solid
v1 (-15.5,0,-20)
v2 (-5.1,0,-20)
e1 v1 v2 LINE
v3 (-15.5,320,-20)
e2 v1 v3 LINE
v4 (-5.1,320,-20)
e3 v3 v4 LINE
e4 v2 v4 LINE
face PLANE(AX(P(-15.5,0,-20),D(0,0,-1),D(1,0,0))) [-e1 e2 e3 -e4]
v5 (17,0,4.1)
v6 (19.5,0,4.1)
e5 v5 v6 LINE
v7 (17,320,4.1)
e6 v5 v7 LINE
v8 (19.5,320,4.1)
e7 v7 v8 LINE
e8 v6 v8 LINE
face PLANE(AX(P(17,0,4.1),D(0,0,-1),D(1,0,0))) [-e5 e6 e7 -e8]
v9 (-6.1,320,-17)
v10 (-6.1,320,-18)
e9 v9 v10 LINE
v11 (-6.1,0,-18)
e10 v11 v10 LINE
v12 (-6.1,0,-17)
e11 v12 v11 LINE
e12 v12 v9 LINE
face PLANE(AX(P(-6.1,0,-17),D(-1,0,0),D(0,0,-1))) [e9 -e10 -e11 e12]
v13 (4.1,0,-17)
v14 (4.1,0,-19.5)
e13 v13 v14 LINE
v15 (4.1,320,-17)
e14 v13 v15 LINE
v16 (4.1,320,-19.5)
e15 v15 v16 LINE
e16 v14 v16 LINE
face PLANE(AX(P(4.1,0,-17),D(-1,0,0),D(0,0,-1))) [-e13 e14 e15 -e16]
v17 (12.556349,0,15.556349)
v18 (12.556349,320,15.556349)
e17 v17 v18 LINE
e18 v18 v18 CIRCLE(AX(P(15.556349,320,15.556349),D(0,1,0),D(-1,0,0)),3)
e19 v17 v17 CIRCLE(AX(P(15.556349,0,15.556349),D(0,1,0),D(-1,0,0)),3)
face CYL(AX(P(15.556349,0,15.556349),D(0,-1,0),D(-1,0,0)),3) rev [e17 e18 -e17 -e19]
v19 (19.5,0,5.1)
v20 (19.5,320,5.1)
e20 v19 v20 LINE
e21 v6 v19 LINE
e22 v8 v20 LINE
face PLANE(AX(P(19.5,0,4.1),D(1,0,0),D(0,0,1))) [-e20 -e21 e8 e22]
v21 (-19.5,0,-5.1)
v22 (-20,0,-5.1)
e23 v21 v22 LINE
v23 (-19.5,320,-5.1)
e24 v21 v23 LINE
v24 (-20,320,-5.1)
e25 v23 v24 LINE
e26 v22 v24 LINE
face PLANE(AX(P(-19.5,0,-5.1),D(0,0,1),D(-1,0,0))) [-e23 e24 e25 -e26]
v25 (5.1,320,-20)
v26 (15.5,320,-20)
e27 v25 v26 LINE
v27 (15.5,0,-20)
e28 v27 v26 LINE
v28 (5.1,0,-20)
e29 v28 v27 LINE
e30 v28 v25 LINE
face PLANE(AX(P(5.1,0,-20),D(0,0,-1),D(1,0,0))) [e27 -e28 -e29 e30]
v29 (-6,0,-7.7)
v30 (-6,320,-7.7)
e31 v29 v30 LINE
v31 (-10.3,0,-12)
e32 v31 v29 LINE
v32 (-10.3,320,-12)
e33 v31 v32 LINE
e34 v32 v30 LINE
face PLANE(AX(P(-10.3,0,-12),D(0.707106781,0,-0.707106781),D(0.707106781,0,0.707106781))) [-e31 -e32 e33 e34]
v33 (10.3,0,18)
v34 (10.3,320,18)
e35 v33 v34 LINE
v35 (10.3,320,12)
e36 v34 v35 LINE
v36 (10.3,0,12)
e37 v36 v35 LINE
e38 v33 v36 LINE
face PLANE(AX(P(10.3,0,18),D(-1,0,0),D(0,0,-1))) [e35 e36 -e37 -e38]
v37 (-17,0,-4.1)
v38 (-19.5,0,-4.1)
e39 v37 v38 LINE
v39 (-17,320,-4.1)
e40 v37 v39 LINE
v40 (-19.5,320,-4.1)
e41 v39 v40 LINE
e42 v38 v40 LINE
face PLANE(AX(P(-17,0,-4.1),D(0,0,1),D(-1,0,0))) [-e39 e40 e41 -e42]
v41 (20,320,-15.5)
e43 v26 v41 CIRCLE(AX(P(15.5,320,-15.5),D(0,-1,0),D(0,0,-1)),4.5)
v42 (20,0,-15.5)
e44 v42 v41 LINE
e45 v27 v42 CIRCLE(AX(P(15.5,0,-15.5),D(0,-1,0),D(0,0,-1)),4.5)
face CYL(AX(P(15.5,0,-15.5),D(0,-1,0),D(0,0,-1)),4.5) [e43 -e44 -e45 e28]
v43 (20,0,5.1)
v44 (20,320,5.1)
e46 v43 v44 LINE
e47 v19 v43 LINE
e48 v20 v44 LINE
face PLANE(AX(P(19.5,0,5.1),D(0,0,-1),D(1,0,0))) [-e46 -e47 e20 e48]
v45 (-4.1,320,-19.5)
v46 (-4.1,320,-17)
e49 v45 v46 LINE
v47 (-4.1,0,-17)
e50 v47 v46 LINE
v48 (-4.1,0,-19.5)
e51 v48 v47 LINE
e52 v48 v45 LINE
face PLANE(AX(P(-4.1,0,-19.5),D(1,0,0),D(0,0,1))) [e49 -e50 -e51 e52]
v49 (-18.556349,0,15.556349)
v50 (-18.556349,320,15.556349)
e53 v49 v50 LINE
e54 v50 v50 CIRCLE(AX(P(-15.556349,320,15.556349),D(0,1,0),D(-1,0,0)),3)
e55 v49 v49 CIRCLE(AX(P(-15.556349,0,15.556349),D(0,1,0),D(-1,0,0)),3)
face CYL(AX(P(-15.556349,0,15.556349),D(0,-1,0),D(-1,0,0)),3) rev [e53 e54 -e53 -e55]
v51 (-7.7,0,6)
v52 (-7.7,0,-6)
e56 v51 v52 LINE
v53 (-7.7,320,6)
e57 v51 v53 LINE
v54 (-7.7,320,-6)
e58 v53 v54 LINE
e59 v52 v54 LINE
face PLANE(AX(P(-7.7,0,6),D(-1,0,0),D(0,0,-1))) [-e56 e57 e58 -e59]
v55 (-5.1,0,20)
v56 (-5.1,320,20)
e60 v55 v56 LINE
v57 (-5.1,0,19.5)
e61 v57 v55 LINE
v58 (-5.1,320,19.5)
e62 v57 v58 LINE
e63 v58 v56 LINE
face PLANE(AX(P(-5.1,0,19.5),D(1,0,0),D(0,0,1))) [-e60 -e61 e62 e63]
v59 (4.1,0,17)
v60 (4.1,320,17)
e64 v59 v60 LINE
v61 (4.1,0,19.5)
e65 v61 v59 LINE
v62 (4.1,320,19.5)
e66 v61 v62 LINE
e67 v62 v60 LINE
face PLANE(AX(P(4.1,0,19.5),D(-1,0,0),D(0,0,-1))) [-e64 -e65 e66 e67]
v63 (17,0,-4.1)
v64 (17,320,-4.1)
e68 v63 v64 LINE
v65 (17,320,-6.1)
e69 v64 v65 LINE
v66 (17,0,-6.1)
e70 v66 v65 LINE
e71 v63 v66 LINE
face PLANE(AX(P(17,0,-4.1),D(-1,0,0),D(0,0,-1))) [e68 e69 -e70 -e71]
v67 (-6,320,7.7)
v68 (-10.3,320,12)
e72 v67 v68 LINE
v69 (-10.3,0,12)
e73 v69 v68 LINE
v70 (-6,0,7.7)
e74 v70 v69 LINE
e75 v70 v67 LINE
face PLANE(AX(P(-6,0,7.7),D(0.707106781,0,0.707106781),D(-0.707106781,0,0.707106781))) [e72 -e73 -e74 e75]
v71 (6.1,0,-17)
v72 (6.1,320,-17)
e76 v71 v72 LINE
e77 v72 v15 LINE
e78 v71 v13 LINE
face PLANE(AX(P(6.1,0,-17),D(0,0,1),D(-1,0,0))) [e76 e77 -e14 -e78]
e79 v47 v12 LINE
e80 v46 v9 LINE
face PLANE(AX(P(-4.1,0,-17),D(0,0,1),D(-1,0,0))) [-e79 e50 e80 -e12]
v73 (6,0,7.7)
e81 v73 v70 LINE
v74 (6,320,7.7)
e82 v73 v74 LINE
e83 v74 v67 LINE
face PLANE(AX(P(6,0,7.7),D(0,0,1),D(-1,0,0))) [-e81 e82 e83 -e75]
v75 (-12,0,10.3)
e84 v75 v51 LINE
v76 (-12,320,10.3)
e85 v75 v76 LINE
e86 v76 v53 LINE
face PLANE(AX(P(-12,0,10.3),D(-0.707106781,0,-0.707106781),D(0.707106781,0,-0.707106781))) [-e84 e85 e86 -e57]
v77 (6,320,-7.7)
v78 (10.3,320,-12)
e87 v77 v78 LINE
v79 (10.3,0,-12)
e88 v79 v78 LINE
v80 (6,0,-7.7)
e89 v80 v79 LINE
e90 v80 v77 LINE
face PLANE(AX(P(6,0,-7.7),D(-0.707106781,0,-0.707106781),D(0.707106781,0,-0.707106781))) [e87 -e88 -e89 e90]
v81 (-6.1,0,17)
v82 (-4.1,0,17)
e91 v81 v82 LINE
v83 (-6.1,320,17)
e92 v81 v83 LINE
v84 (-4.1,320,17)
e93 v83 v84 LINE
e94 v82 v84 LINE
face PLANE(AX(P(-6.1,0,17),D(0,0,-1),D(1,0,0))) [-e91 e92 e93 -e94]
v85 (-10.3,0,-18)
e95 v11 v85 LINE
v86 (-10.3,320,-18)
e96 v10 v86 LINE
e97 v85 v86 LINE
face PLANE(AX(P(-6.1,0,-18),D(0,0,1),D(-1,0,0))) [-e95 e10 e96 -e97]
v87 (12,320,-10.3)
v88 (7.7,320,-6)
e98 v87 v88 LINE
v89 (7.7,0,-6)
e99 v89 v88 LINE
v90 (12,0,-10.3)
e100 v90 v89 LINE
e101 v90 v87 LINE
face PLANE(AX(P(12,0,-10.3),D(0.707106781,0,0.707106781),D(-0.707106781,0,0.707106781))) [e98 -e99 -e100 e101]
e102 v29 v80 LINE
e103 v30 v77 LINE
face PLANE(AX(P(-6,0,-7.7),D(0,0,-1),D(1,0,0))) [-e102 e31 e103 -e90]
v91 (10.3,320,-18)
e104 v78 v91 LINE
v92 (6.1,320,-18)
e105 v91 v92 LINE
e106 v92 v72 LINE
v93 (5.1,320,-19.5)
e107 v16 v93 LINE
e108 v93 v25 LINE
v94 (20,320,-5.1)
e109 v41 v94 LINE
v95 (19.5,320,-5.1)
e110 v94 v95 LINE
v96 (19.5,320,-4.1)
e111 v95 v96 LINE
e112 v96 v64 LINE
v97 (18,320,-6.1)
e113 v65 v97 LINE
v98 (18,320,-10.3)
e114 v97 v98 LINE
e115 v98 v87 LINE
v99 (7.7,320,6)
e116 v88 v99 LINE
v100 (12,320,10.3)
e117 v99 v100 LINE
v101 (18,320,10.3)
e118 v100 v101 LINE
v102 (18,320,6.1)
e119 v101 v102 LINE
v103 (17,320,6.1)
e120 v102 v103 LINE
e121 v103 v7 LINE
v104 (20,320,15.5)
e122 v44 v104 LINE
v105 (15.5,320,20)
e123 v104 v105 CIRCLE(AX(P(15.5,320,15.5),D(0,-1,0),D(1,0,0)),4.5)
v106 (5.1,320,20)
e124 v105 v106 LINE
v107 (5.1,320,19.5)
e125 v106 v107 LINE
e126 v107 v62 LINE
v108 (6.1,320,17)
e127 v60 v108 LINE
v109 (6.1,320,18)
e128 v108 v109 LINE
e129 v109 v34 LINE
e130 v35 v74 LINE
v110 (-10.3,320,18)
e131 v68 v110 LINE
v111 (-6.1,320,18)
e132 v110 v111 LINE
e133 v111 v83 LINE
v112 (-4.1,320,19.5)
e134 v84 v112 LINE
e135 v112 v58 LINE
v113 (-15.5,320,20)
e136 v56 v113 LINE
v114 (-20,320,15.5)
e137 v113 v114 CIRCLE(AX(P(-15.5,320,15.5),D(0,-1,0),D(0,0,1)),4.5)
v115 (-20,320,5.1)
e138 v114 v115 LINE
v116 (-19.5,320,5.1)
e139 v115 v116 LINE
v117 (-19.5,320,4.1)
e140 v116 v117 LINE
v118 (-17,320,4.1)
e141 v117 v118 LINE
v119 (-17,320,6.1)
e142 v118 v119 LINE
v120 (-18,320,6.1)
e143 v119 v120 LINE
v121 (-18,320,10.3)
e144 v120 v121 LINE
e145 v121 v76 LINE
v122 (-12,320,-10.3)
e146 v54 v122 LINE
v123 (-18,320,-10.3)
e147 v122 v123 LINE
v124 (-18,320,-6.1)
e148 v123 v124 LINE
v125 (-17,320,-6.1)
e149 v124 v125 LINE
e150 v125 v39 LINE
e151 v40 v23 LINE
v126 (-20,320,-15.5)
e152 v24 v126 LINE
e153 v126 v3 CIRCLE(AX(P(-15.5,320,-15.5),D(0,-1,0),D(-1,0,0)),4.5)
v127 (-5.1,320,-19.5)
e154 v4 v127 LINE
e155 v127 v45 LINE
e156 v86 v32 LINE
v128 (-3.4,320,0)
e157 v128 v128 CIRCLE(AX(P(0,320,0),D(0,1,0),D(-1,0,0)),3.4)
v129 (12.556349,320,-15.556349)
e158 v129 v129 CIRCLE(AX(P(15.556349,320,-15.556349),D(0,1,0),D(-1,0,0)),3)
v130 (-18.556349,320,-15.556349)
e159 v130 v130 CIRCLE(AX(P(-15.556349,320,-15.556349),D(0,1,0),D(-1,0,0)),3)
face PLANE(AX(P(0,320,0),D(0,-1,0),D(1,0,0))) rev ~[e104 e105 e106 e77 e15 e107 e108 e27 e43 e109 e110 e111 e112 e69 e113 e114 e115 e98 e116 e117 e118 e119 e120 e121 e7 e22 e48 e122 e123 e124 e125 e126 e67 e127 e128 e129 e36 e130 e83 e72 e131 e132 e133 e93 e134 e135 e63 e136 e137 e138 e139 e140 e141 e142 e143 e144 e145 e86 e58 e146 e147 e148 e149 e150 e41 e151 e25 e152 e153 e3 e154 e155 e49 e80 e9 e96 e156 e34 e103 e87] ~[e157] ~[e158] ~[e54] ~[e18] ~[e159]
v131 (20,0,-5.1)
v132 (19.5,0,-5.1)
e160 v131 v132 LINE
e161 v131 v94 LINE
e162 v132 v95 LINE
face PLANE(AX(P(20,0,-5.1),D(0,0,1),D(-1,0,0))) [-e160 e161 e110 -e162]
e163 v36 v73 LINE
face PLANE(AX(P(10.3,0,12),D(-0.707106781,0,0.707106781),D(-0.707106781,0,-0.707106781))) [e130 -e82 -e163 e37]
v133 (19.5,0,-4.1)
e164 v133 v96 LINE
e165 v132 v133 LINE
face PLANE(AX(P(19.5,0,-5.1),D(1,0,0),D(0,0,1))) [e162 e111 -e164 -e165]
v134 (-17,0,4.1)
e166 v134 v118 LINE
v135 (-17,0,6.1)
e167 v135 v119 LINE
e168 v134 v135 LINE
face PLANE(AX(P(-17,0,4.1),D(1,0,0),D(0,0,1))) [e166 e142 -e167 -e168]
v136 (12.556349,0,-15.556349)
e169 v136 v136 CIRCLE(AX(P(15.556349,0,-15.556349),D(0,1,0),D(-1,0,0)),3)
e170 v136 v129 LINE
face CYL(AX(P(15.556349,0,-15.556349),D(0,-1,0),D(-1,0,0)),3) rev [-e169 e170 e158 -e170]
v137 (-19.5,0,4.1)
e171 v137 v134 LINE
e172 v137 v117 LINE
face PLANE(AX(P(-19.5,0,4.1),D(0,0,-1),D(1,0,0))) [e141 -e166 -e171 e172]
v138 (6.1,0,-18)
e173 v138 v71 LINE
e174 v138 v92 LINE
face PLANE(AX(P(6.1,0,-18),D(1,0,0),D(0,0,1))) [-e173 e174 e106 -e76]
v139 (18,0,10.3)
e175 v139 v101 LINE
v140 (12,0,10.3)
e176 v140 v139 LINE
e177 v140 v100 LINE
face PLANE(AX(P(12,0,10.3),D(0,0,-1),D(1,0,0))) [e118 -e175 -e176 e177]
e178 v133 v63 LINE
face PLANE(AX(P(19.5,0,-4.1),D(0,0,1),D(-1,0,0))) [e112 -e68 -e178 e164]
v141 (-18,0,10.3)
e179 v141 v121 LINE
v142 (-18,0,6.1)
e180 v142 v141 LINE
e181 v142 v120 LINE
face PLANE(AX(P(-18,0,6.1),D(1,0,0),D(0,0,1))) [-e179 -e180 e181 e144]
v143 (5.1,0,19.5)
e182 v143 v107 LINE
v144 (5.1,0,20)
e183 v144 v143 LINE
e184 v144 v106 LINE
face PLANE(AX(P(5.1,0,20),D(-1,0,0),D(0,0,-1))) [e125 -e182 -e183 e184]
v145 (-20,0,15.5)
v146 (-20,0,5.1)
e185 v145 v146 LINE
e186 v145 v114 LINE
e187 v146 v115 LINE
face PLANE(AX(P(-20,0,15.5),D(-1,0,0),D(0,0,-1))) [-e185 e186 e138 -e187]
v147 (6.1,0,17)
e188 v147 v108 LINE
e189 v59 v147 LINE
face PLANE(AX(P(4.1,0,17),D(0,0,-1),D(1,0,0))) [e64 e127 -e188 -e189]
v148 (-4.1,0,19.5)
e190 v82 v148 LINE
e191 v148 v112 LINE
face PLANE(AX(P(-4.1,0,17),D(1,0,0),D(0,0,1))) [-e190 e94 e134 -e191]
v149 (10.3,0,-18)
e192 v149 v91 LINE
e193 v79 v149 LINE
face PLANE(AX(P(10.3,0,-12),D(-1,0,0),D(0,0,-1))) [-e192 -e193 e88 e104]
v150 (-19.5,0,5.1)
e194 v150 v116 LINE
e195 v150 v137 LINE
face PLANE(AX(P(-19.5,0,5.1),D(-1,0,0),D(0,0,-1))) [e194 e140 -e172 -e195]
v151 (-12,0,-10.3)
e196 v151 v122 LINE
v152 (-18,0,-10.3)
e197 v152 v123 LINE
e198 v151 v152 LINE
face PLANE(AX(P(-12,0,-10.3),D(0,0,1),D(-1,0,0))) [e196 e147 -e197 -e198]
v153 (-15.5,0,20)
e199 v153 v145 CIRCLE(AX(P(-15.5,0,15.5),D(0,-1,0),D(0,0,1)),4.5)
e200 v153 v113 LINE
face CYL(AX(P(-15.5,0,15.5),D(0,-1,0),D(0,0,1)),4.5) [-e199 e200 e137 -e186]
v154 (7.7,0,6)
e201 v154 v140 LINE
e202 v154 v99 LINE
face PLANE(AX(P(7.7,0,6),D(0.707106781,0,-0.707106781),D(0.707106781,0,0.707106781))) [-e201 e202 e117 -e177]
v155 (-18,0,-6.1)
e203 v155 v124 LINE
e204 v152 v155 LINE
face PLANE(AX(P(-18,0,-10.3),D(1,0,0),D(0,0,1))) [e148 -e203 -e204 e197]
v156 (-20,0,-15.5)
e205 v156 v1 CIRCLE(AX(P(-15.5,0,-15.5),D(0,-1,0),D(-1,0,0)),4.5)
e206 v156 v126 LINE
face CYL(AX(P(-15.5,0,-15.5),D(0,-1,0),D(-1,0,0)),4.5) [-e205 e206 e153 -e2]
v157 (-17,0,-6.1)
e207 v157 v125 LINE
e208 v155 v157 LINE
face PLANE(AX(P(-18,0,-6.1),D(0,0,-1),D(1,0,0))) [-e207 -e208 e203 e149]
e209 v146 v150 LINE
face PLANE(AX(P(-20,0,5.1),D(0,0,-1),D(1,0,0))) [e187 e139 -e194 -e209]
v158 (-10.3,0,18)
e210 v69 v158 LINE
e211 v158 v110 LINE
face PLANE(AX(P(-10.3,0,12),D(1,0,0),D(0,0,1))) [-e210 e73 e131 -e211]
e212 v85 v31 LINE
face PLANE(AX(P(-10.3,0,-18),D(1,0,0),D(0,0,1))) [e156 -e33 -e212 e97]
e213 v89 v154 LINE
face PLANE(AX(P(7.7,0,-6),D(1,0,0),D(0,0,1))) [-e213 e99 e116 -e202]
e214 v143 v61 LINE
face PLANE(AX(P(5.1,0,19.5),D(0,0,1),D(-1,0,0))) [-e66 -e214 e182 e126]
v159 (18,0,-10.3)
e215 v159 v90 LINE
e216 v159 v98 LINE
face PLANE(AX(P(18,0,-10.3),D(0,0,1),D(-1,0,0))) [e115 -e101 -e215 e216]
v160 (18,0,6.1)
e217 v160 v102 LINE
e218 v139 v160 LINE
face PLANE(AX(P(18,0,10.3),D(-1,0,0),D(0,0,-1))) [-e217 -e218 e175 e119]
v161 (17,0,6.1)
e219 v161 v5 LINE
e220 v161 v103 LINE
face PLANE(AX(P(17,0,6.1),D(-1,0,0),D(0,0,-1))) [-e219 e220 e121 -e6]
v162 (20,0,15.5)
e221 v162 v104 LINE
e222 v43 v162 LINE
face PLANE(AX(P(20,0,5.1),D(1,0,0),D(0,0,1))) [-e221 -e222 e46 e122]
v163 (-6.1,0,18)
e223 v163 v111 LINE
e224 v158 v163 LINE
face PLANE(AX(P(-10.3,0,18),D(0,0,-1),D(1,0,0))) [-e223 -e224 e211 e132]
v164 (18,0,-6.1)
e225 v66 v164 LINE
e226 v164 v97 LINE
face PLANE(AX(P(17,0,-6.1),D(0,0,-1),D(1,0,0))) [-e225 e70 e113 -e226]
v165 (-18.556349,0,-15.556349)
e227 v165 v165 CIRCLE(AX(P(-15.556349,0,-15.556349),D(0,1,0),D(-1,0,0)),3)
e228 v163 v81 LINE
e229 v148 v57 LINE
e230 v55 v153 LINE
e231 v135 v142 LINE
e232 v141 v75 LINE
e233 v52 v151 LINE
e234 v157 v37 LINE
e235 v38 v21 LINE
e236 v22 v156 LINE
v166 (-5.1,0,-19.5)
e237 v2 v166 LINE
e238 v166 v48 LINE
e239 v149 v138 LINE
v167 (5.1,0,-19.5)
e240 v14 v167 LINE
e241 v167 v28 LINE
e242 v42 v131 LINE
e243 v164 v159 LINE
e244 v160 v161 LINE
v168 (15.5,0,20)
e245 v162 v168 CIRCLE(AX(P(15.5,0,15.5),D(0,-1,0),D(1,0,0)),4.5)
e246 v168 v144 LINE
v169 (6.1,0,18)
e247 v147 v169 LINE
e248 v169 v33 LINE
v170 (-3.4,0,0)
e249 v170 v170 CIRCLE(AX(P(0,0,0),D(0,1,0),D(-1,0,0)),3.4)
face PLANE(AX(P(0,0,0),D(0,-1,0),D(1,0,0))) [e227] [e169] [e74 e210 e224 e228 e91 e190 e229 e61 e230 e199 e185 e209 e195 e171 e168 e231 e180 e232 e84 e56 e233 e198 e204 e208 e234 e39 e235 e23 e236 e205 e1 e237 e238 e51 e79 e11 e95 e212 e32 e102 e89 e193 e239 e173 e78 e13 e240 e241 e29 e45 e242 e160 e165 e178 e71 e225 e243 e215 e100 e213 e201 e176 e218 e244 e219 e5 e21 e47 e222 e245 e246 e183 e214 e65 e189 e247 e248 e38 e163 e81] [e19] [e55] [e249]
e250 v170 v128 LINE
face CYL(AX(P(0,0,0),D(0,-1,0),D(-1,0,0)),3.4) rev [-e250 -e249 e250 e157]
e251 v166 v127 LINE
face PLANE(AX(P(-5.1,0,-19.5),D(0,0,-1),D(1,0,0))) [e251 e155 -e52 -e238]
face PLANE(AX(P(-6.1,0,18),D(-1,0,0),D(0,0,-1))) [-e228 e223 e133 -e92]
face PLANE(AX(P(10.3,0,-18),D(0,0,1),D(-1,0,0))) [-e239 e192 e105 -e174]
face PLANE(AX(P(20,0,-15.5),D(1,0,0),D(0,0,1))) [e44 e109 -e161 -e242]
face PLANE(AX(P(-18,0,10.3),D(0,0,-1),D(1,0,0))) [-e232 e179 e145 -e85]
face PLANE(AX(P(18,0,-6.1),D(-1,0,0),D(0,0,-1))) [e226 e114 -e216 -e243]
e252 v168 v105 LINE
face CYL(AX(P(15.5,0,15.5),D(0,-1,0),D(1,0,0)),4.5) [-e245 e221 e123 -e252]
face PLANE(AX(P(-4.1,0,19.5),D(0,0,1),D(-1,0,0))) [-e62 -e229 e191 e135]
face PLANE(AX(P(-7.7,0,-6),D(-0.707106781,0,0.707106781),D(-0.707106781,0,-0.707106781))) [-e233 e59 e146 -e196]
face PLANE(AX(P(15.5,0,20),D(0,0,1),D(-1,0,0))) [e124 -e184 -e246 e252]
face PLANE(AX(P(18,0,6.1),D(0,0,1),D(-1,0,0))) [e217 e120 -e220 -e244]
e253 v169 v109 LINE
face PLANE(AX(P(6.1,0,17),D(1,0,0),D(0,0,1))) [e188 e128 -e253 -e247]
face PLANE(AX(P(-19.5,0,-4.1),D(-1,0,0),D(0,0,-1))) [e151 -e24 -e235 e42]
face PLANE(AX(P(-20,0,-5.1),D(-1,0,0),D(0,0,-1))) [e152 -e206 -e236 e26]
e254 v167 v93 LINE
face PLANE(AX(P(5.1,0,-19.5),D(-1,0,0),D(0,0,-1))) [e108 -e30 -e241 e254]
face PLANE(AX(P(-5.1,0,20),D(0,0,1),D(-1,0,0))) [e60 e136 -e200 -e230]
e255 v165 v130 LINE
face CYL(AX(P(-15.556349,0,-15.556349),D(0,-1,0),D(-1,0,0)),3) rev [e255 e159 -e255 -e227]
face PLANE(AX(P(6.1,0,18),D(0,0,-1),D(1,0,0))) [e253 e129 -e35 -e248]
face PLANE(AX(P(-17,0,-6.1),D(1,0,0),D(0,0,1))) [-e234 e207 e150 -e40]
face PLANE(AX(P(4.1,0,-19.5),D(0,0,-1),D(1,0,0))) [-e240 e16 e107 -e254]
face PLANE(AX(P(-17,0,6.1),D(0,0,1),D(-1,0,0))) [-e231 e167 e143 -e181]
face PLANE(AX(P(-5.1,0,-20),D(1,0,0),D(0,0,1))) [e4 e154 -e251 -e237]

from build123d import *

# Parameters (mm, degrees)
SKETCH16_R     = 3.4
SKETCH16_R_2   = 3
MEMBER_1_DEPTH = 320


with BuildPart() as part:
    # Sketch16 → Member 1 (new body)
    with BuildSketch(Plane(origin=(0, 0, 0), x_dir=(-1, 0, 0), z_dir=(0, 1, 0))):
        with BuildLine():
            Line((-5.1, 20), (-5.1, 19.5))
            Line((-5.1, 19.5), (-4.1, 19.5))
            Line((-4.1, 19.5), (-4.1, 17))
            Line((-4.1, 17), (-6.1, 17))
            Line((-6.1, 17), (-6.1, 18))
            Line((-6.1, 18), (-10.3, 18))
            Line((-10.3, 18), (-10.3, 12))
            Line((-10.3, 12), (-6, 7.7))
            Line((-6, 7.7), (6, 7.7))
            Line((6, 7.7), (10.3, 12))
            Line((10.3, 12), (10.3, 18))
            Line((10.3, 18), (6.1, 18))
            Line((6.1, 18), (6.1, 17))
            Line((6.1, 17), (4.1, 17))
            Line((4.1, 17), (4.1, 19.5))
            Line((4.1, 19.5), (5.1, 19.5))
            Line((5.1, 19.5), (5.1, 20))
            Line((5.1, 20), (15.5, 20))
            ThreePointArc((15.5, 20), (18.681980515, 18.681980515), (20, 15.5))
            Line((20, 15.5), (20, 5.1))
            Line((20, 5.1), (19.5, 5.1))
            Line((19.5, 5.1), (19.5, 4.1))
            Line((19.5, 4.1), (17, 4.1))
            Line((17, 4.1), (17, 6.1))
            Line((17, 6.1), (18, 6.1))
            Line((18, 6.1), (18, 10.3))
            Line((18, 10.3), (12, 10.3))
            Line((12, 10.3), (7.7, 6))
            Line((7.7, 6), (7.7, -6))
            Line((7.7, -6), (12, -10.3))
            Line((12, -10.3), (18, -10.3))
            Line((18, -10.3), (18, -6.1))
            Line((18, -6.1), (17, -6.1))
            Line((17, -6.1), (17, -4.1))
            Line((17, -4.1), (19.5, -4.1))
            Line((19.5, -4.1), (19.5, -5.1))
            Line((19.5, -5.1), (20, -5.1))
            Line((20, -5.1), (20, -15.5))
            ThreePointArc((20, -15.5), (18.681980515, -18.681980515), (15.5, -20))
            Line((15.5, -20), (5.1, -20))
            Line((5.1, -20), (5.1, -19.5))
            Line((5.1, -19.5), (4.1, -19.5))
            Line((4.1, -19.5), (4.1, -17))
            Line((4.1, -17), (6.1, -17))
            Line((6.1, -17), (6.1, -18))
            Line((6.1, -18), (10.3, -18))
            Line((10.3, -18), (10.3, -12))
            Line((10.3, -12), (6, -7.7))
            Line((6, -7.7), (-6, -7.7))
            Line((-6, -7.7), (-10.3, -12))
            Line((-10.3, -12), (-10.3, -18))
            Line((-10.3, -18), (-6.1, -18))
            Line((-6.1, -18), (-6.1, -17))
            Line((-6.1, -17), (-4.1, -17))
            Line((-4.1, -17), (-4.1, -19.5))
            Line((-4.1, -19.5), (-5.1, -19.5))
            Line((-5.1, -19.5), (-5.1, -20))
            Line((-5.1, -20), (-15.5, -20))
            ThreePointArc((-15.5, -20), (-18.681980515, -18.681980515), (-20, -15.5))
            Line((-20, -15.5), (-20, -5.1))
            Line((-20, -5.1), (-19.5, -5.1))
            Line((-19.5, -5.1), (-19.5, -4.1))
            Line((-19.5, -4.1), (-17, -4.1))
            Line((-17, -4.1), (-17, -6.1))
            Line((-17, -6.1), (-18, -6.1))
            Line((-18, -6.1), (-18, -10.3))
            Line((-18, -10.3), (-12, -10.3))
            Line((-12, -10.3), (-7.7, -6))
            Line((-7.7, -6), (-7.7, 6))
            Line((-7.7, 6), (-12, 10.3))
            Line((-12, 10.3), (-18, 10.3))
            Line((-18, 10.3), (-18, 6.1))
            Line((-18, 6.1), (-17, 6.1))
            Line((-17, 6.1), (-17, 4.1))
            Line((-17, 4.1), (-19.5, 4.1))
            Line((-19.5, 4.1), (-19.5, 5.1))
            Line((-19.5, 5.1), (-20, 5.1))
            Line((-20, 5.1), (-20, 15.5))
            ThreePointArc((-20, 15.5), (-18.681980515, 18.681980515), (-15.5, 20))
            Line((-15.5, 20), (-5.1, 20))
        make_face()
        Circle(SKETCH16_R, mode=Mode.SUBTRACT)
        with Locations((-15.556349186, 15.556349186)):
            Circle(SKETCH16_R_2, mode=Mode.SUBTRACT)
        with Locations((15.556349186, 15.556349186)):
            Circle(SKETCH16_R_2, mode=Mode.SUBTRACT)
        with Locations((15.556349186, -15.556349186)):
            Circle(SKETCH16_R_2, mode=Mode.SUBTRACT)
        with Locations((-15.556349186, -15.556349186)):
            Circle(SKETCH16_R_2, mode=Mode.SUBTRACT)
    extrude(amount=MEMBER_1_DEPTH)


solid = part.part
